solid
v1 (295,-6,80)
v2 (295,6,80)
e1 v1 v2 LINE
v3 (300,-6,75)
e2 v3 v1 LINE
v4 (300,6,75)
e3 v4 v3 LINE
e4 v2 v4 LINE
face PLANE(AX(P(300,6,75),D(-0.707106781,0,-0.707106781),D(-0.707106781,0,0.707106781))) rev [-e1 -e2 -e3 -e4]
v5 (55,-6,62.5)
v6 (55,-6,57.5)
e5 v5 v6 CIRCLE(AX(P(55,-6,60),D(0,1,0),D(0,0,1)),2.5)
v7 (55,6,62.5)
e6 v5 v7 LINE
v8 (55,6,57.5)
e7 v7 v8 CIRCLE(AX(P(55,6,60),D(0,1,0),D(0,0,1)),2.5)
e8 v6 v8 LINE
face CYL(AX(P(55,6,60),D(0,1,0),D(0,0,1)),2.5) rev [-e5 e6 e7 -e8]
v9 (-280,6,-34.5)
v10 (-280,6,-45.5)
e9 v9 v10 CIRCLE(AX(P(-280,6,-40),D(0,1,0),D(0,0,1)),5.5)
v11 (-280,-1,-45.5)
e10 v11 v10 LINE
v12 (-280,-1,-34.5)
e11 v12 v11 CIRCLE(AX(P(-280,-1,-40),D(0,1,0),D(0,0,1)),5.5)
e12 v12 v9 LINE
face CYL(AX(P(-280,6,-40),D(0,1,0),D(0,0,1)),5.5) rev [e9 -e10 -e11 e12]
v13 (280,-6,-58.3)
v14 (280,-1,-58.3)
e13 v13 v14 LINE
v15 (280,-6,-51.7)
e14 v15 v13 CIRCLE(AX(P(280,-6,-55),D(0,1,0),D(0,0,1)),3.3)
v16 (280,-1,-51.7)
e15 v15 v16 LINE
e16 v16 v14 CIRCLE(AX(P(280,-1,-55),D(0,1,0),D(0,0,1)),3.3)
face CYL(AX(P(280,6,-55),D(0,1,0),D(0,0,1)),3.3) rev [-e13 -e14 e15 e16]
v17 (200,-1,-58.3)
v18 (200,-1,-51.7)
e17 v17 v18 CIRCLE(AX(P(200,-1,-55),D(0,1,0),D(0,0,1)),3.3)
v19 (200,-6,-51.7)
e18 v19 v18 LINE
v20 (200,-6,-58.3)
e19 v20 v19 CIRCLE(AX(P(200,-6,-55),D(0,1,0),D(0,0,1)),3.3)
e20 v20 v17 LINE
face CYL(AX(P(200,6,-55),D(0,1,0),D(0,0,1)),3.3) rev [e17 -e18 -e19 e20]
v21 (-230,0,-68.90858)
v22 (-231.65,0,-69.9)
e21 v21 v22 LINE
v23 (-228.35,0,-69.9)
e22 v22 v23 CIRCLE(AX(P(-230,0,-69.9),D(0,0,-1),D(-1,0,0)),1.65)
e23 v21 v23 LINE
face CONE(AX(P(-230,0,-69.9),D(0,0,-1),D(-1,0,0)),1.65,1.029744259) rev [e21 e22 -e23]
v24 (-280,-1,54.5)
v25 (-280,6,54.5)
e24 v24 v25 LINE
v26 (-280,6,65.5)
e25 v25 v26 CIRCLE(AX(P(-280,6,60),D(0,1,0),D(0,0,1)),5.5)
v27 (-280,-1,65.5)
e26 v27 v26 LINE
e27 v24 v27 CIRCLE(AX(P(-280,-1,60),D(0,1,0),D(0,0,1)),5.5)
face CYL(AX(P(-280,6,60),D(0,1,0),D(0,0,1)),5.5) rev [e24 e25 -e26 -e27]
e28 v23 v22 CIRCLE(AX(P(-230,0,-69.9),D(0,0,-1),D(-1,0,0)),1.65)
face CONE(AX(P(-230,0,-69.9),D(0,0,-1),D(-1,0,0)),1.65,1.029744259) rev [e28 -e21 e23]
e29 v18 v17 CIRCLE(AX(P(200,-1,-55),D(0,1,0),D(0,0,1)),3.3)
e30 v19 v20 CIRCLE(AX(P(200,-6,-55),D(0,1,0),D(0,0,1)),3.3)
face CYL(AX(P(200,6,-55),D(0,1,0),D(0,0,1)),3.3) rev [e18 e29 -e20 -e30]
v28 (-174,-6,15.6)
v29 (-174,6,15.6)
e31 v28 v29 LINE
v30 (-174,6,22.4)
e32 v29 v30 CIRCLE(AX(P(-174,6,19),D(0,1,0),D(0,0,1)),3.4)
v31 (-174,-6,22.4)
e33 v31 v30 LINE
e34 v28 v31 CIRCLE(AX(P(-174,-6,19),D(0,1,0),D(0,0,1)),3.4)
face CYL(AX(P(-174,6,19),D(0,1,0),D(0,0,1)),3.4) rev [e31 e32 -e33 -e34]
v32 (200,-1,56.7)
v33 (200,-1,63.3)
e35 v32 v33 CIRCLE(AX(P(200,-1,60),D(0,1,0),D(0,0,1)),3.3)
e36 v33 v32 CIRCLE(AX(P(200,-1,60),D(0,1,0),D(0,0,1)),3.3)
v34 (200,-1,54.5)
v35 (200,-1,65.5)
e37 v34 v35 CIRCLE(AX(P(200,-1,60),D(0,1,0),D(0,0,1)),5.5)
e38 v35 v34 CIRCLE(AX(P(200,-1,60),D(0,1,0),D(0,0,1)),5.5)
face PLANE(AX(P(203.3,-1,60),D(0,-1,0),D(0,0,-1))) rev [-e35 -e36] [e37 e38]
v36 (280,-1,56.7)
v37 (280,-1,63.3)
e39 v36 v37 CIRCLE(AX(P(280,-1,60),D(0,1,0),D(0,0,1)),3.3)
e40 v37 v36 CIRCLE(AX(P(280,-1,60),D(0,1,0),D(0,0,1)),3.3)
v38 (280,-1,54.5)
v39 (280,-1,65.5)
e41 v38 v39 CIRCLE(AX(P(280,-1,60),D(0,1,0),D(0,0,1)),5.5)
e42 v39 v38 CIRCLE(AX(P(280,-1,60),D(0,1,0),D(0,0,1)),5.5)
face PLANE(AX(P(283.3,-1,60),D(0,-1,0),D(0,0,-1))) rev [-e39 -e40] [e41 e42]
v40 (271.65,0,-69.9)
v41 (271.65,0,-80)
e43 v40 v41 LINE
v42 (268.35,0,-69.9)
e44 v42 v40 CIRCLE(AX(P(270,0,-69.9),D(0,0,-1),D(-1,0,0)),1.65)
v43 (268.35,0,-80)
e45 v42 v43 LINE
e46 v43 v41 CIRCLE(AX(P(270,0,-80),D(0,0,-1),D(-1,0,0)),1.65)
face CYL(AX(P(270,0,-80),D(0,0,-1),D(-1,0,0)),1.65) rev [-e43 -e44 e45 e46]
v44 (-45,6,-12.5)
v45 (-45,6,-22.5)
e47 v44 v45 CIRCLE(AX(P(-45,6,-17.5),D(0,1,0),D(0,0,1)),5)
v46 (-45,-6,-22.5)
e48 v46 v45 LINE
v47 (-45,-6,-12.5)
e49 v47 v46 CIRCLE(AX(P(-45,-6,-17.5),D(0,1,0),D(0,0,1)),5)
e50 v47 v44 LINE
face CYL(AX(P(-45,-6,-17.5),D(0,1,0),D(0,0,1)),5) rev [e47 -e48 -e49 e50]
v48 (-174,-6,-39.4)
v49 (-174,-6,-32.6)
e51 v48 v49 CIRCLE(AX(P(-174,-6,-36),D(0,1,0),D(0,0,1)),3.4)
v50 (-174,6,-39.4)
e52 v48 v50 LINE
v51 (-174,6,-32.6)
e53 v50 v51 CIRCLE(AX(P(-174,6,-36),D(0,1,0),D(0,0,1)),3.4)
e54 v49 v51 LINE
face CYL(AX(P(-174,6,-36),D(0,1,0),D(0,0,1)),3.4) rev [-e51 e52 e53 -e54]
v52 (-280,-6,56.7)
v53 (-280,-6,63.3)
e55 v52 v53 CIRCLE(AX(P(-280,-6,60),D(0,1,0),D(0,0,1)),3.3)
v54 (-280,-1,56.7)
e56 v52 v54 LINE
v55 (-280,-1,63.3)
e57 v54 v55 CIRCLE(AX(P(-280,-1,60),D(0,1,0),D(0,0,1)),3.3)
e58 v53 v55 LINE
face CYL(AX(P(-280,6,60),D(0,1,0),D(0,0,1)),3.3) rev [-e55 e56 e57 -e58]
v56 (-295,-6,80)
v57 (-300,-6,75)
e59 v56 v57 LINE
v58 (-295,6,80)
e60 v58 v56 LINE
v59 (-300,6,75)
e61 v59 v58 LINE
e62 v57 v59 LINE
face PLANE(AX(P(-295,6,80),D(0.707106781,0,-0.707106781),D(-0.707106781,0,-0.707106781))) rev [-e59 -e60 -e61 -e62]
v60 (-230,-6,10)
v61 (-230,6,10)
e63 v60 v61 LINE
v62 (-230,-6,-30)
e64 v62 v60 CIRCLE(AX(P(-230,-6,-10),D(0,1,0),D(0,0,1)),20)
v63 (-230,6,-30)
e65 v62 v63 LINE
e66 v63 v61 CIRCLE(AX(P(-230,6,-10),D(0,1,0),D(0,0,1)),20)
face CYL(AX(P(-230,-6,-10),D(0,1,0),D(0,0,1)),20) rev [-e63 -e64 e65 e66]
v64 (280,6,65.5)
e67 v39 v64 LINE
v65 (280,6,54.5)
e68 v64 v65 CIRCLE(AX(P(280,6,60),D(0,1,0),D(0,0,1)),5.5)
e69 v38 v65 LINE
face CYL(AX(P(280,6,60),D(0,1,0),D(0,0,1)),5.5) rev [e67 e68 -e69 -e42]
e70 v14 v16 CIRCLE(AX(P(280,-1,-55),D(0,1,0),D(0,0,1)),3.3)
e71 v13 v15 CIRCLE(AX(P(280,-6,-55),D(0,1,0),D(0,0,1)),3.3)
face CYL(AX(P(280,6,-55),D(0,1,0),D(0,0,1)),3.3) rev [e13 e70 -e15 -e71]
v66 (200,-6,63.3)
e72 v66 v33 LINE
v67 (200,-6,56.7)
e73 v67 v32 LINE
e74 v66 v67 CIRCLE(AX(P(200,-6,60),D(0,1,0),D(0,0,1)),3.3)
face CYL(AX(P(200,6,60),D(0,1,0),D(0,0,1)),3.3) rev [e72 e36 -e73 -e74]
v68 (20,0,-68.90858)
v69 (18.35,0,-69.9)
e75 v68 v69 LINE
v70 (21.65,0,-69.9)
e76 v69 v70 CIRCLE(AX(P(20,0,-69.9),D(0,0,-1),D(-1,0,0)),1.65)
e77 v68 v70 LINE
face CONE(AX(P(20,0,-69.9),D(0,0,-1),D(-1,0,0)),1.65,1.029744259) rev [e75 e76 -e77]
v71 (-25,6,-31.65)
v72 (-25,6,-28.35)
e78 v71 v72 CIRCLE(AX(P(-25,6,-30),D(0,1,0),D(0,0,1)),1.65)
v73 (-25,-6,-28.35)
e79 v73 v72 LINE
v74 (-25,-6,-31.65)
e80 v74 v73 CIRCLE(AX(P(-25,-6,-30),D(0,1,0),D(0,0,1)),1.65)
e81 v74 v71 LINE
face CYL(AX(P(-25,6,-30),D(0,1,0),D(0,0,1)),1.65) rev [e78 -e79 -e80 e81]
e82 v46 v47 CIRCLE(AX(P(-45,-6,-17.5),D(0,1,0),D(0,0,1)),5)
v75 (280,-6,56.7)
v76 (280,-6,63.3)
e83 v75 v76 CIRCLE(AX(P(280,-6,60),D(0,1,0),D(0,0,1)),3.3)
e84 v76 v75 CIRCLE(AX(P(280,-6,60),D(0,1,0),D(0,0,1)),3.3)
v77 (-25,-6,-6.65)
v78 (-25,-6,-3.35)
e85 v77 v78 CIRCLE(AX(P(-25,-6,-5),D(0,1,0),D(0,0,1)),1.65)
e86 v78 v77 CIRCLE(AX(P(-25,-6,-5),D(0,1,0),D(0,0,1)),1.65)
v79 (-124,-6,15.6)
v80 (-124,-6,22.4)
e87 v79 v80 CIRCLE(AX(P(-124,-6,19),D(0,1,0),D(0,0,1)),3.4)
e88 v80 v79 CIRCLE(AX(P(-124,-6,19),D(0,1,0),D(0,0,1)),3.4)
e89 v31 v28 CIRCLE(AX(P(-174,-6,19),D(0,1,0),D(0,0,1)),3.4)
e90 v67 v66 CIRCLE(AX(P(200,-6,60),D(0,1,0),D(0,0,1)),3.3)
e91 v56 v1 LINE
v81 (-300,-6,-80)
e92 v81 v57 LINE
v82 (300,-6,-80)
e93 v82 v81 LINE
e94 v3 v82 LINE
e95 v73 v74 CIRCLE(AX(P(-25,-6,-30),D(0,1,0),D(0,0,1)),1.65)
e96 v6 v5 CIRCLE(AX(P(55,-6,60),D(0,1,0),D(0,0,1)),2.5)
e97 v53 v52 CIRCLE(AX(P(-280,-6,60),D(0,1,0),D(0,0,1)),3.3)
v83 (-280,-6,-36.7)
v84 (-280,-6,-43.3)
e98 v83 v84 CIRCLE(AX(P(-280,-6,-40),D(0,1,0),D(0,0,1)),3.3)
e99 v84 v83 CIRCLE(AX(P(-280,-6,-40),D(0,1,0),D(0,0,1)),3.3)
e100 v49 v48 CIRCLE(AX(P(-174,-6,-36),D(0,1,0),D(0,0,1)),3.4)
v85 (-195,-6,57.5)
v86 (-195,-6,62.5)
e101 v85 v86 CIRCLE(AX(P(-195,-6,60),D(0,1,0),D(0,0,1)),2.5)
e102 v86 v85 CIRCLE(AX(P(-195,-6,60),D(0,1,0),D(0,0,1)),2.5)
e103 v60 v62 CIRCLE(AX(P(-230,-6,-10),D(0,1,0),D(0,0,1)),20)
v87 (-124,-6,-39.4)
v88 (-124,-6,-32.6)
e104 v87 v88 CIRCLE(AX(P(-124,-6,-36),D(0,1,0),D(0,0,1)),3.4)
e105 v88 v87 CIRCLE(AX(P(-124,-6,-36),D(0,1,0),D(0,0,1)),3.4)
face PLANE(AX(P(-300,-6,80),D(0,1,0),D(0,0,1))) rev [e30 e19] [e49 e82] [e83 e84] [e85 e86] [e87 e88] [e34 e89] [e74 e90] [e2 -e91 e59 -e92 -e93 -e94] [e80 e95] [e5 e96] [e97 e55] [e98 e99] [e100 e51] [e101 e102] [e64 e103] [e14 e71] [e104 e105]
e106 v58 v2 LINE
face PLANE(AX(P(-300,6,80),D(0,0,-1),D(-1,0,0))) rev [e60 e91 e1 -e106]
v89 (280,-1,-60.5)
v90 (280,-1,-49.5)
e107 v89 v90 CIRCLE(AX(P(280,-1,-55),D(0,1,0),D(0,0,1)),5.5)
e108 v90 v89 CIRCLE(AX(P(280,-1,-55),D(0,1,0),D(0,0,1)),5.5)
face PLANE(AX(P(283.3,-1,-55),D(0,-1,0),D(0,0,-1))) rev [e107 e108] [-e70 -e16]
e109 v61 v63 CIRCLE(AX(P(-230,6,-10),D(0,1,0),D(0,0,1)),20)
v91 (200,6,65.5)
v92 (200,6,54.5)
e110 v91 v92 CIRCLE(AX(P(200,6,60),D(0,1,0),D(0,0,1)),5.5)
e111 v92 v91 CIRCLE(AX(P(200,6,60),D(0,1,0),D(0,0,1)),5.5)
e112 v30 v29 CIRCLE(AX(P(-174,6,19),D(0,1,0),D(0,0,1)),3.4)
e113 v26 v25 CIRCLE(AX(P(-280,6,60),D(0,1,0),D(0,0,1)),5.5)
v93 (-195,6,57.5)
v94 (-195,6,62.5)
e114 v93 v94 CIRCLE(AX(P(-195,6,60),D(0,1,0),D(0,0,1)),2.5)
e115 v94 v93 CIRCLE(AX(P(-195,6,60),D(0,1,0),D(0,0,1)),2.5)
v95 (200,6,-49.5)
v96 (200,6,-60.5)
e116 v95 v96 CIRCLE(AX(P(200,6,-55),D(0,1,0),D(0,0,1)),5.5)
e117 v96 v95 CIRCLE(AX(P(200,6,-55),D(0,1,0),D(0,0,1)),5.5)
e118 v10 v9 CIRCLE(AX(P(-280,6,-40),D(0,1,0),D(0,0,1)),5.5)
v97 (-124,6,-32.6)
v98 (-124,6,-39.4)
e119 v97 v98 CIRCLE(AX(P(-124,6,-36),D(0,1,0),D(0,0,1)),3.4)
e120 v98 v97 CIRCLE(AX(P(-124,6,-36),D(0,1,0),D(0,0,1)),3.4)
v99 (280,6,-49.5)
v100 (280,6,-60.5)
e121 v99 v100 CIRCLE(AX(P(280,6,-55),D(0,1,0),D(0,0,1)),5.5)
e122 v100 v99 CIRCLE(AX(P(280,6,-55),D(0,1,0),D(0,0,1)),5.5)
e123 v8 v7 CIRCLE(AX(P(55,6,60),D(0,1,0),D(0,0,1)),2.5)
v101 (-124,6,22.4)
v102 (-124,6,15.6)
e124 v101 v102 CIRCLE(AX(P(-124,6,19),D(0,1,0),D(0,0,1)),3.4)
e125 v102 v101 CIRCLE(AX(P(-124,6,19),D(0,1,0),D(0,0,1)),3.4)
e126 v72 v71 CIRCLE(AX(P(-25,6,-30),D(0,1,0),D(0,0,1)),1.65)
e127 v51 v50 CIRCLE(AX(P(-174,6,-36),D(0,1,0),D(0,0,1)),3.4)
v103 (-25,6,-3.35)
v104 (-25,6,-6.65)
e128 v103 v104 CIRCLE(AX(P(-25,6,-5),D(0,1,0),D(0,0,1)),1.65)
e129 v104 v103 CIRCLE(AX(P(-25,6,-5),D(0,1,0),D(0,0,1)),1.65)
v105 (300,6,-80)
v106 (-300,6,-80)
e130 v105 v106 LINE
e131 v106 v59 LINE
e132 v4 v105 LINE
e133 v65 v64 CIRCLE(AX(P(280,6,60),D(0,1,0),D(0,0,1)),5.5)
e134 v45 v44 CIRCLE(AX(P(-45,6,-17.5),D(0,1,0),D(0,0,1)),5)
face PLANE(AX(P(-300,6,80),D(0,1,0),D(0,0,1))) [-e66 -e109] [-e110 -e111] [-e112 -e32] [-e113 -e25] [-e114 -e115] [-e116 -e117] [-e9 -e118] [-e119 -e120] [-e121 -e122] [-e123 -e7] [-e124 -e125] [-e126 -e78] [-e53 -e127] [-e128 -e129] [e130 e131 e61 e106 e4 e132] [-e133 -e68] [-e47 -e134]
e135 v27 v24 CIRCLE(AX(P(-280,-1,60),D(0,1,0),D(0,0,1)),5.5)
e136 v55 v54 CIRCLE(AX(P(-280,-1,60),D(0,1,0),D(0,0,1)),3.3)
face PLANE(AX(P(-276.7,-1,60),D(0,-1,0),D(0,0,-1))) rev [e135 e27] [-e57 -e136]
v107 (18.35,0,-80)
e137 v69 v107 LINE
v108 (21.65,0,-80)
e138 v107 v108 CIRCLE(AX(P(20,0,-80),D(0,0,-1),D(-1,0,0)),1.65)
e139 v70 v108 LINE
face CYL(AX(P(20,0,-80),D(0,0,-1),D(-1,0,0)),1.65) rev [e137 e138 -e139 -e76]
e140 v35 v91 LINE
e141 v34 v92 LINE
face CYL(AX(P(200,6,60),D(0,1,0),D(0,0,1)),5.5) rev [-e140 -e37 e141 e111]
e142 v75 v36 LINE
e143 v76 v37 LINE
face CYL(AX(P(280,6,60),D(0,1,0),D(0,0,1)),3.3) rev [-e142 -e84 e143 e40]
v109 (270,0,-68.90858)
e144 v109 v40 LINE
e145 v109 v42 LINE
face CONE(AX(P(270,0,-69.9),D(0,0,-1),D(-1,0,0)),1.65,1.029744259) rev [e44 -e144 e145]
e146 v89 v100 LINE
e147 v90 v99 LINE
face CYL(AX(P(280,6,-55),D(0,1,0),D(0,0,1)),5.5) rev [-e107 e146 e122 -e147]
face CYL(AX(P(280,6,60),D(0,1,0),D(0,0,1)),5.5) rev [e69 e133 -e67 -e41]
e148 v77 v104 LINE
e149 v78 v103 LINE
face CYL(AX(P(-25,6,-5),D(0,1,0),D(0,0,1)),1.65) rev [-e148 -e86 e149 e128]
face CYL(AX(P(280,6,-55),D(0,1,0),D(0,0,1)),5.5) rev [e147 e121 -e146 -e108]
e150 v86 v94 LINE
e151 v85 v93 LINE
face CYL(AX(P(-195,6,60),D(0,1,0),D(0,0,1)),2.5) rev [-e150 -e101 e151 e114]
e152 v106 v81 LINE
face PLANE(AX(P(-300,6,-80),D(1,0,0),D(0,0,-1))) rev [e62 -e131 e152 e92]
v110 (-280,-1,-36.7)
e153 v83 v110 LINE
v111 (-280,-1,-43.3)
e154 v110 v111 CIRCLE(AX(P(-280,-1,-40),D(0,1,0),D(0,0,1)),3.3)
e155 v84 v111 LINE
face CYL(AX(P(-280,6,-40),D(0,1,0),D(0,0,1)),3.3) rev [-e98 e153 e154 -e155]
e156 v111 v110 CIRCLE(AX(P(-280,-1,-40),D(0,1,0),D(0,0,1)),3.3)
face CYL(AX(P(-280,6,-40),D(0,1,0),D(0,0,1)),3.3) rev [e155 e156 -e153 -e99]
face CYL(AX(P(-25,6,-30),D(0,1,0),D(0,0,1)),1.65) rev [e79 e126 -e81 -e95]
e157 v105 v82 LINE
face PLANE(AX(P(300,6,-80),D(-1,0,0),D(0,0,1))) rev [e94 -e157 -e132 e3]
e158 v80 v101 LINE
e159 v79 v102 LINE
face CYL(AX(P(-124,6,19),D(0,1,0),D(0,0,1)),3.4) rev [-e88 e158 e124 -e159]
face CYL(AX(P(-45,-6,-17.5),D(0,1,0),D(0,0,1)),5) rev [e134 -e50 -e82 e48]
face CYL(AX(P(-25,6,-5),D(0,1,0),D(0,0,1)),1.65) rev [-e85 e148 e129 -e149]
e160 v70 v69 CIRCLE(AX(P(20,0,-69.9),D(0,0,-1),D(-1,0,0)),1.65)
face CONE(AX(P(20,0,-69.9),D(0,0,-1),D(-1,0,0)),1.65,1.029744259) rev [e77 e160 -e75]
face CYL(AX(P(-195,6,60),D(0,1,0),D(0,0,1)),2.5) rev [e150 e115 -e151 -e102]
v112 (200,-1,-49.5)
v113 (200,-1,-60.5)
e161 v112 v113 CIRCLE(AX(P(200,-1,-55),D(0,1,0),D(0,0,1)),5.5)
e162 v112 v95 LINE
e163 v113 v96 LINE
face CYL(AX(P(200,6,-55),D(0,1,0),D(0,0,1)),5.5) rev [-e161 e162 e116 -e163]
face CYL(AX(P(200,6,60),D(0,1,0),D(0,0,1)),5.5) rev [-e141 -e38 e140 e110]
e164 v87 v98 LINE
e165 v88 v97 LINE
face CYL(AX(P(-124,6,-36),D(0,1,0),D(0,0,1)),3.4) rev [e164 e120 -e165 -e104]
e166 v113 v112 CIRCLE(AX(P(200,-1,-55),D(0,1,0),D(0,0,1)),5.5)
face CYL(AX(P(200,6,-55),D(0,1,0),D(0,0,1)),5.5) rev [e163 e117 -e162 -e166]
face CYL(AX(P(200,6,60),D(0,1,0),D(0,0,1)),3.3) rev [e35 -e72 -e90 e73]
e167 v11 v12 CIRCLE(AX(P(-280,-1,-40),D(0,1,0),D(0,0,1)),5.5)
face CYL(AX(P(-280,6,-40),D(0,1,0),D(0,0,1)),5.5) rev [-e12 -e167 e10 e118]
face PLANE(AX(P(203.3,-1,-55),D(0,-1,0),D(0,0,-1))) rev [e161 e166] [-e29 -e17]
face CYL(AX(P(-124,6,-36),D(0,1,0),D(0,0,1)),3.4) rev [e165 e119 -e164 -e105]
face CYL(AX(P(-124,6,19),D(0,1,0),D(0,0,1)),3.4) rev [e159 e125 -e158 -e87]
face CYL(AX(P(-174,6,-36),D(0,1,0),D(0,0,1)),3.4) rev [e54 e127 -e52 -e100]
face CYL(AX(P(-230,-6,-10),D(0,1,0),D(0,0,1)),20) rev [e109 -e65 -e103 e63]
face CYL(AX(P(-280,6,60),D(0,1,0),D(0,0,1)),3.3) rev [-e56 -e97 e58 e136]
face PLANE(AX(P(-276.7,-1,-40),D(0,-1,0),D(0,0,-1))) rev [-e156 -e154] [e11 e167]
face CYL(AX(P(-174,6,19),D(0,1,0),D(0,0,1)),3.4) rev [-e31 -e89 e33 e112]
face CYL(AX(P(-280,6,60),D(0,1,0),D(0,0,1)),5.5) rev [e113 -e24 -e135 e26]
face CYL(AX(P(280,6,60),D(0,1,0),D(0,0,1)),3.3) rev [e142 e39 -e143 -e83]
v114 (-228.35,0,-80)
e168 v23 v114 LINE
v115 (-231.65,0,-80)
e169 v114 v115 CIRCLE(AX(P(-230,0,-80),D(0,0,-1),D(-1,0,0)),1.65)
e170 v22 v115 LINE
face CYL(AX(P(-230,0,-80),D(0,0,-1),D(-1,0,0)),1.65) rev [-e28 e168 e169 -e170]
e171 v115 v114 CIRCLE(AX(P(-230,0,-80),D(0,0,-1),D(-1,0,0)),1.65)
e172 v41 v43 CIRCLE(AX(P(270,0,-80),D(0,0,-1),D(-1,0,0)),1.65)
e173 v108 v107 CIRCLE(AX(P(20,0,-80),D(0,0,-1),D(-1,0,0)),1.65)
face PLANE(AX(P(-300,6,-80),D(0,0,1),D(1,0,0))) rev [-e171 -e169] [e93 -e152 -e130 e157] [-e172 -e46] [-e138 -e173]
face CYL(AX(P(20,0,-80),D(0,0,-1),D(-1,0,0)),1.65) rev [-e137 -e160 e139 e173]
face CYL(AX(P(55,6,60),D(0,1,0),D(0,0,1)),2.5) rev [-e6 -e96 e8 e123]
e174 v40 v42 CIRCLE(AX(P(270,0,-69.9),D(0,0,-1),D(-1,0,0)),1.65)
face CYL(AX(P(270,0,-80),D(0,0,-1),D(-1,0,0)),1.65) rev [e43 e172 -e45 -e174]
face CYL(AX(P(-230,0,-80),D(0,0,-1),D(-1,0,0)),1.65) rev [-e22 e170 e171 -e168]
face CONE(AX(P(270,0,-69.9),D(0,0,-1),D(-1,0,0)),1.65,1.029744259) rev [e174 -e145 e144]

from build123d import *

# Parameters (mm, degrees)
SKETCH1_W                                         = 600
SKETCH1_H                                         = 160
EXTRUDE1_DEPTH                                    = 6
M6_SOCKET_HEAD_CAP_SCREW_COUNTERBORE1_D           = 6.6
M6_SOCKET_HEAD_CAP_SCREW_COUNTERBORE1_CBORE_D     = 11
M6_SOCKET_HEAD_CAP_SCREW_COUNTERBORE1_CBORE_DEPTH = 7
M4_TAPPED_HOLE1_D                                 = 3.3
M4_TAPPED_HOLE1_DEPTH                             = 10.1
M4_TAPPED_HOLE1_TIP                               = 0.991420021
M8_TAPPED_HOLE1_D                                 = 6.8
M6_TAPPED_HOLE2_D                                 = 5
SKETCH10_R                                        = 20
CUT_EXTRUDE1_DEPTH                                = 311.715303775
M4_TAPPED_HOLE2_D                                 = 3.3
M4_TAPPED_HOLE2_DEPTH                             = 12
M4_TAPPED_HOLE2_TIP                               = 0.991420021
CHAMFER1_SIZE                                     = 5
SKETCH13_R                                        = 5
CUT_EXTRUDE2_DEPTH                                = 311.715303775


with BuildPart() as part:
    # Sketch1 → Extrude1 (new, symmetric)
    with BuildSketch(Plane(origin=(0, 0, 0), x_dir=(1, 0, 0), z_dir=(0, 1, 0))):
        Rectangle(SKETCH1_W, SKETCH1_H)
    extrude(amount=EXTRUDE1_DEPTH, both=True)

    # M6 Socket Head Cap Screw Counterbore1 (through all)
    with Locations(Plane(origin=(-280, 6, 60), x_dir=(0, 0, 1), z_dir=(0, 1, 0))):
        with Locations((0, 0), (-100, 0), (0, 480), (-115, 480), (-115, 560), (0, 560)):
            CounterBoreHole(M6_SOCKET_HEAD_CAP_SCREW_COUNTERBORE1_D / 2, M6_SOCKET_HEAD_CAP_SCREW_COUNTERBORE1_CBORE_D / 2, M6_SOCKET_HEAD_CAP_SCREW_COUNTERBORE1_CBORE_DEPTH)

    # M4 Tapped Hole1
    with Locations(Plane(origin=(270, 0, -80), x_dir=(-1, 0, 0), z_dir=(0, 0, -1))):
        with Locations((0, 0), (250, 0), (500, 0)):
            Hole(M4_TAPPED_HOLE1_D / 2, depth=M4_TAPPED_HOLE1_DEPTH)
            with Locations((0, 0, -(M4_TAPPED_HOLE1_DEPTH + M4_TAPPED_HOLE1_TIP / 2))):  # 118° drill point
                Cone(0, M4_TAPPED_HOLE1_D / 2, M4_TAPPED_HOLE1_TIP, mode=Mode.SUBTRACT)

    # M8 Tapped Hole1 (through all)
    with Locations(Plane(origin=(-174, 6, 19), x_dir=(0, 0, 1), z_dir=(0, 1, 0))):
        with Locations((0, 0), (0, 50), (-55, 50), (-55, 0)):
            Hole(M8_TAPPED_HOLE1_D / 2)

    # M6 Tapped Hole2 (through all)
    with Locations(Plane(origin=(55, 6, 60), x_dir=(0, 0, 1), z_dir=(0, 1, 0))):
        with Locations((0, 0), (0, -250)):
            Hole(M6_TAPPED_HOLE2_D / 2)

    # Sketch10 → Cut-Extrude1 (cut, through all)
    with BuildSketch(Plane(origin=(0, 6, 0), x_dir=(1, 0, 0), z_dir=(0, 1, 0))):
        with Locations(Location((-230, 10, 0), (0, 0, 270))):
            Circle(SKETCH10_R)
    extrude(amount=-CUT_EXTRUDE1_DEPTH, mode=Mode.SUBTRACT)

    # M4 Tapped Hole2
    with Locations(Plane(origin=(-25, 6, -5), x_dir=(0, 0, 1), z_dir=(0, 1, 0))):
        with Locations((0, 0), (-25, 0)):
            Hole(M4_TAPPED_HOLE2_D / 2, depth=M4_TAPPED_HOLE2_DEPTH)
            with Locations((0, 0, -(M4_TAPPED_HOLE2_DEPTH + M4_TAPPED_HOLE2_TIP / 2))):  # 118° drill point
                Cone(0, M4_TAPPED_HOLE2_D / 2, M4_TAPPED_HOLE2_TIP, mode=Mode.SUBTRACT)

    # Chamfer1
    chamfer1_edges = [part.edges().sort_by_distance(p)[0] for p in [
        (300, 0, 80),
        (-300, 0, 80),
    ]]
    chamfer(chamfer1_edges, length=CHAMFER1_SIZE)

    # Sketch13 → Cut-Extrude2 (cut, through all)
    with BuildSketch(Plane(origin=(0, 6, 0), x_dir=(1, 0, 0), z_dir=(0, 1, 0))):
        with Locations(Location((-45, 17.5, 0), (0, 0, 270))):
            Circle(SKETCH13_R)
    extrude(amount=-CUT_EXTRUDE2_DEPTH, mode=Mode.SUBTRACT)


solid = part.part
